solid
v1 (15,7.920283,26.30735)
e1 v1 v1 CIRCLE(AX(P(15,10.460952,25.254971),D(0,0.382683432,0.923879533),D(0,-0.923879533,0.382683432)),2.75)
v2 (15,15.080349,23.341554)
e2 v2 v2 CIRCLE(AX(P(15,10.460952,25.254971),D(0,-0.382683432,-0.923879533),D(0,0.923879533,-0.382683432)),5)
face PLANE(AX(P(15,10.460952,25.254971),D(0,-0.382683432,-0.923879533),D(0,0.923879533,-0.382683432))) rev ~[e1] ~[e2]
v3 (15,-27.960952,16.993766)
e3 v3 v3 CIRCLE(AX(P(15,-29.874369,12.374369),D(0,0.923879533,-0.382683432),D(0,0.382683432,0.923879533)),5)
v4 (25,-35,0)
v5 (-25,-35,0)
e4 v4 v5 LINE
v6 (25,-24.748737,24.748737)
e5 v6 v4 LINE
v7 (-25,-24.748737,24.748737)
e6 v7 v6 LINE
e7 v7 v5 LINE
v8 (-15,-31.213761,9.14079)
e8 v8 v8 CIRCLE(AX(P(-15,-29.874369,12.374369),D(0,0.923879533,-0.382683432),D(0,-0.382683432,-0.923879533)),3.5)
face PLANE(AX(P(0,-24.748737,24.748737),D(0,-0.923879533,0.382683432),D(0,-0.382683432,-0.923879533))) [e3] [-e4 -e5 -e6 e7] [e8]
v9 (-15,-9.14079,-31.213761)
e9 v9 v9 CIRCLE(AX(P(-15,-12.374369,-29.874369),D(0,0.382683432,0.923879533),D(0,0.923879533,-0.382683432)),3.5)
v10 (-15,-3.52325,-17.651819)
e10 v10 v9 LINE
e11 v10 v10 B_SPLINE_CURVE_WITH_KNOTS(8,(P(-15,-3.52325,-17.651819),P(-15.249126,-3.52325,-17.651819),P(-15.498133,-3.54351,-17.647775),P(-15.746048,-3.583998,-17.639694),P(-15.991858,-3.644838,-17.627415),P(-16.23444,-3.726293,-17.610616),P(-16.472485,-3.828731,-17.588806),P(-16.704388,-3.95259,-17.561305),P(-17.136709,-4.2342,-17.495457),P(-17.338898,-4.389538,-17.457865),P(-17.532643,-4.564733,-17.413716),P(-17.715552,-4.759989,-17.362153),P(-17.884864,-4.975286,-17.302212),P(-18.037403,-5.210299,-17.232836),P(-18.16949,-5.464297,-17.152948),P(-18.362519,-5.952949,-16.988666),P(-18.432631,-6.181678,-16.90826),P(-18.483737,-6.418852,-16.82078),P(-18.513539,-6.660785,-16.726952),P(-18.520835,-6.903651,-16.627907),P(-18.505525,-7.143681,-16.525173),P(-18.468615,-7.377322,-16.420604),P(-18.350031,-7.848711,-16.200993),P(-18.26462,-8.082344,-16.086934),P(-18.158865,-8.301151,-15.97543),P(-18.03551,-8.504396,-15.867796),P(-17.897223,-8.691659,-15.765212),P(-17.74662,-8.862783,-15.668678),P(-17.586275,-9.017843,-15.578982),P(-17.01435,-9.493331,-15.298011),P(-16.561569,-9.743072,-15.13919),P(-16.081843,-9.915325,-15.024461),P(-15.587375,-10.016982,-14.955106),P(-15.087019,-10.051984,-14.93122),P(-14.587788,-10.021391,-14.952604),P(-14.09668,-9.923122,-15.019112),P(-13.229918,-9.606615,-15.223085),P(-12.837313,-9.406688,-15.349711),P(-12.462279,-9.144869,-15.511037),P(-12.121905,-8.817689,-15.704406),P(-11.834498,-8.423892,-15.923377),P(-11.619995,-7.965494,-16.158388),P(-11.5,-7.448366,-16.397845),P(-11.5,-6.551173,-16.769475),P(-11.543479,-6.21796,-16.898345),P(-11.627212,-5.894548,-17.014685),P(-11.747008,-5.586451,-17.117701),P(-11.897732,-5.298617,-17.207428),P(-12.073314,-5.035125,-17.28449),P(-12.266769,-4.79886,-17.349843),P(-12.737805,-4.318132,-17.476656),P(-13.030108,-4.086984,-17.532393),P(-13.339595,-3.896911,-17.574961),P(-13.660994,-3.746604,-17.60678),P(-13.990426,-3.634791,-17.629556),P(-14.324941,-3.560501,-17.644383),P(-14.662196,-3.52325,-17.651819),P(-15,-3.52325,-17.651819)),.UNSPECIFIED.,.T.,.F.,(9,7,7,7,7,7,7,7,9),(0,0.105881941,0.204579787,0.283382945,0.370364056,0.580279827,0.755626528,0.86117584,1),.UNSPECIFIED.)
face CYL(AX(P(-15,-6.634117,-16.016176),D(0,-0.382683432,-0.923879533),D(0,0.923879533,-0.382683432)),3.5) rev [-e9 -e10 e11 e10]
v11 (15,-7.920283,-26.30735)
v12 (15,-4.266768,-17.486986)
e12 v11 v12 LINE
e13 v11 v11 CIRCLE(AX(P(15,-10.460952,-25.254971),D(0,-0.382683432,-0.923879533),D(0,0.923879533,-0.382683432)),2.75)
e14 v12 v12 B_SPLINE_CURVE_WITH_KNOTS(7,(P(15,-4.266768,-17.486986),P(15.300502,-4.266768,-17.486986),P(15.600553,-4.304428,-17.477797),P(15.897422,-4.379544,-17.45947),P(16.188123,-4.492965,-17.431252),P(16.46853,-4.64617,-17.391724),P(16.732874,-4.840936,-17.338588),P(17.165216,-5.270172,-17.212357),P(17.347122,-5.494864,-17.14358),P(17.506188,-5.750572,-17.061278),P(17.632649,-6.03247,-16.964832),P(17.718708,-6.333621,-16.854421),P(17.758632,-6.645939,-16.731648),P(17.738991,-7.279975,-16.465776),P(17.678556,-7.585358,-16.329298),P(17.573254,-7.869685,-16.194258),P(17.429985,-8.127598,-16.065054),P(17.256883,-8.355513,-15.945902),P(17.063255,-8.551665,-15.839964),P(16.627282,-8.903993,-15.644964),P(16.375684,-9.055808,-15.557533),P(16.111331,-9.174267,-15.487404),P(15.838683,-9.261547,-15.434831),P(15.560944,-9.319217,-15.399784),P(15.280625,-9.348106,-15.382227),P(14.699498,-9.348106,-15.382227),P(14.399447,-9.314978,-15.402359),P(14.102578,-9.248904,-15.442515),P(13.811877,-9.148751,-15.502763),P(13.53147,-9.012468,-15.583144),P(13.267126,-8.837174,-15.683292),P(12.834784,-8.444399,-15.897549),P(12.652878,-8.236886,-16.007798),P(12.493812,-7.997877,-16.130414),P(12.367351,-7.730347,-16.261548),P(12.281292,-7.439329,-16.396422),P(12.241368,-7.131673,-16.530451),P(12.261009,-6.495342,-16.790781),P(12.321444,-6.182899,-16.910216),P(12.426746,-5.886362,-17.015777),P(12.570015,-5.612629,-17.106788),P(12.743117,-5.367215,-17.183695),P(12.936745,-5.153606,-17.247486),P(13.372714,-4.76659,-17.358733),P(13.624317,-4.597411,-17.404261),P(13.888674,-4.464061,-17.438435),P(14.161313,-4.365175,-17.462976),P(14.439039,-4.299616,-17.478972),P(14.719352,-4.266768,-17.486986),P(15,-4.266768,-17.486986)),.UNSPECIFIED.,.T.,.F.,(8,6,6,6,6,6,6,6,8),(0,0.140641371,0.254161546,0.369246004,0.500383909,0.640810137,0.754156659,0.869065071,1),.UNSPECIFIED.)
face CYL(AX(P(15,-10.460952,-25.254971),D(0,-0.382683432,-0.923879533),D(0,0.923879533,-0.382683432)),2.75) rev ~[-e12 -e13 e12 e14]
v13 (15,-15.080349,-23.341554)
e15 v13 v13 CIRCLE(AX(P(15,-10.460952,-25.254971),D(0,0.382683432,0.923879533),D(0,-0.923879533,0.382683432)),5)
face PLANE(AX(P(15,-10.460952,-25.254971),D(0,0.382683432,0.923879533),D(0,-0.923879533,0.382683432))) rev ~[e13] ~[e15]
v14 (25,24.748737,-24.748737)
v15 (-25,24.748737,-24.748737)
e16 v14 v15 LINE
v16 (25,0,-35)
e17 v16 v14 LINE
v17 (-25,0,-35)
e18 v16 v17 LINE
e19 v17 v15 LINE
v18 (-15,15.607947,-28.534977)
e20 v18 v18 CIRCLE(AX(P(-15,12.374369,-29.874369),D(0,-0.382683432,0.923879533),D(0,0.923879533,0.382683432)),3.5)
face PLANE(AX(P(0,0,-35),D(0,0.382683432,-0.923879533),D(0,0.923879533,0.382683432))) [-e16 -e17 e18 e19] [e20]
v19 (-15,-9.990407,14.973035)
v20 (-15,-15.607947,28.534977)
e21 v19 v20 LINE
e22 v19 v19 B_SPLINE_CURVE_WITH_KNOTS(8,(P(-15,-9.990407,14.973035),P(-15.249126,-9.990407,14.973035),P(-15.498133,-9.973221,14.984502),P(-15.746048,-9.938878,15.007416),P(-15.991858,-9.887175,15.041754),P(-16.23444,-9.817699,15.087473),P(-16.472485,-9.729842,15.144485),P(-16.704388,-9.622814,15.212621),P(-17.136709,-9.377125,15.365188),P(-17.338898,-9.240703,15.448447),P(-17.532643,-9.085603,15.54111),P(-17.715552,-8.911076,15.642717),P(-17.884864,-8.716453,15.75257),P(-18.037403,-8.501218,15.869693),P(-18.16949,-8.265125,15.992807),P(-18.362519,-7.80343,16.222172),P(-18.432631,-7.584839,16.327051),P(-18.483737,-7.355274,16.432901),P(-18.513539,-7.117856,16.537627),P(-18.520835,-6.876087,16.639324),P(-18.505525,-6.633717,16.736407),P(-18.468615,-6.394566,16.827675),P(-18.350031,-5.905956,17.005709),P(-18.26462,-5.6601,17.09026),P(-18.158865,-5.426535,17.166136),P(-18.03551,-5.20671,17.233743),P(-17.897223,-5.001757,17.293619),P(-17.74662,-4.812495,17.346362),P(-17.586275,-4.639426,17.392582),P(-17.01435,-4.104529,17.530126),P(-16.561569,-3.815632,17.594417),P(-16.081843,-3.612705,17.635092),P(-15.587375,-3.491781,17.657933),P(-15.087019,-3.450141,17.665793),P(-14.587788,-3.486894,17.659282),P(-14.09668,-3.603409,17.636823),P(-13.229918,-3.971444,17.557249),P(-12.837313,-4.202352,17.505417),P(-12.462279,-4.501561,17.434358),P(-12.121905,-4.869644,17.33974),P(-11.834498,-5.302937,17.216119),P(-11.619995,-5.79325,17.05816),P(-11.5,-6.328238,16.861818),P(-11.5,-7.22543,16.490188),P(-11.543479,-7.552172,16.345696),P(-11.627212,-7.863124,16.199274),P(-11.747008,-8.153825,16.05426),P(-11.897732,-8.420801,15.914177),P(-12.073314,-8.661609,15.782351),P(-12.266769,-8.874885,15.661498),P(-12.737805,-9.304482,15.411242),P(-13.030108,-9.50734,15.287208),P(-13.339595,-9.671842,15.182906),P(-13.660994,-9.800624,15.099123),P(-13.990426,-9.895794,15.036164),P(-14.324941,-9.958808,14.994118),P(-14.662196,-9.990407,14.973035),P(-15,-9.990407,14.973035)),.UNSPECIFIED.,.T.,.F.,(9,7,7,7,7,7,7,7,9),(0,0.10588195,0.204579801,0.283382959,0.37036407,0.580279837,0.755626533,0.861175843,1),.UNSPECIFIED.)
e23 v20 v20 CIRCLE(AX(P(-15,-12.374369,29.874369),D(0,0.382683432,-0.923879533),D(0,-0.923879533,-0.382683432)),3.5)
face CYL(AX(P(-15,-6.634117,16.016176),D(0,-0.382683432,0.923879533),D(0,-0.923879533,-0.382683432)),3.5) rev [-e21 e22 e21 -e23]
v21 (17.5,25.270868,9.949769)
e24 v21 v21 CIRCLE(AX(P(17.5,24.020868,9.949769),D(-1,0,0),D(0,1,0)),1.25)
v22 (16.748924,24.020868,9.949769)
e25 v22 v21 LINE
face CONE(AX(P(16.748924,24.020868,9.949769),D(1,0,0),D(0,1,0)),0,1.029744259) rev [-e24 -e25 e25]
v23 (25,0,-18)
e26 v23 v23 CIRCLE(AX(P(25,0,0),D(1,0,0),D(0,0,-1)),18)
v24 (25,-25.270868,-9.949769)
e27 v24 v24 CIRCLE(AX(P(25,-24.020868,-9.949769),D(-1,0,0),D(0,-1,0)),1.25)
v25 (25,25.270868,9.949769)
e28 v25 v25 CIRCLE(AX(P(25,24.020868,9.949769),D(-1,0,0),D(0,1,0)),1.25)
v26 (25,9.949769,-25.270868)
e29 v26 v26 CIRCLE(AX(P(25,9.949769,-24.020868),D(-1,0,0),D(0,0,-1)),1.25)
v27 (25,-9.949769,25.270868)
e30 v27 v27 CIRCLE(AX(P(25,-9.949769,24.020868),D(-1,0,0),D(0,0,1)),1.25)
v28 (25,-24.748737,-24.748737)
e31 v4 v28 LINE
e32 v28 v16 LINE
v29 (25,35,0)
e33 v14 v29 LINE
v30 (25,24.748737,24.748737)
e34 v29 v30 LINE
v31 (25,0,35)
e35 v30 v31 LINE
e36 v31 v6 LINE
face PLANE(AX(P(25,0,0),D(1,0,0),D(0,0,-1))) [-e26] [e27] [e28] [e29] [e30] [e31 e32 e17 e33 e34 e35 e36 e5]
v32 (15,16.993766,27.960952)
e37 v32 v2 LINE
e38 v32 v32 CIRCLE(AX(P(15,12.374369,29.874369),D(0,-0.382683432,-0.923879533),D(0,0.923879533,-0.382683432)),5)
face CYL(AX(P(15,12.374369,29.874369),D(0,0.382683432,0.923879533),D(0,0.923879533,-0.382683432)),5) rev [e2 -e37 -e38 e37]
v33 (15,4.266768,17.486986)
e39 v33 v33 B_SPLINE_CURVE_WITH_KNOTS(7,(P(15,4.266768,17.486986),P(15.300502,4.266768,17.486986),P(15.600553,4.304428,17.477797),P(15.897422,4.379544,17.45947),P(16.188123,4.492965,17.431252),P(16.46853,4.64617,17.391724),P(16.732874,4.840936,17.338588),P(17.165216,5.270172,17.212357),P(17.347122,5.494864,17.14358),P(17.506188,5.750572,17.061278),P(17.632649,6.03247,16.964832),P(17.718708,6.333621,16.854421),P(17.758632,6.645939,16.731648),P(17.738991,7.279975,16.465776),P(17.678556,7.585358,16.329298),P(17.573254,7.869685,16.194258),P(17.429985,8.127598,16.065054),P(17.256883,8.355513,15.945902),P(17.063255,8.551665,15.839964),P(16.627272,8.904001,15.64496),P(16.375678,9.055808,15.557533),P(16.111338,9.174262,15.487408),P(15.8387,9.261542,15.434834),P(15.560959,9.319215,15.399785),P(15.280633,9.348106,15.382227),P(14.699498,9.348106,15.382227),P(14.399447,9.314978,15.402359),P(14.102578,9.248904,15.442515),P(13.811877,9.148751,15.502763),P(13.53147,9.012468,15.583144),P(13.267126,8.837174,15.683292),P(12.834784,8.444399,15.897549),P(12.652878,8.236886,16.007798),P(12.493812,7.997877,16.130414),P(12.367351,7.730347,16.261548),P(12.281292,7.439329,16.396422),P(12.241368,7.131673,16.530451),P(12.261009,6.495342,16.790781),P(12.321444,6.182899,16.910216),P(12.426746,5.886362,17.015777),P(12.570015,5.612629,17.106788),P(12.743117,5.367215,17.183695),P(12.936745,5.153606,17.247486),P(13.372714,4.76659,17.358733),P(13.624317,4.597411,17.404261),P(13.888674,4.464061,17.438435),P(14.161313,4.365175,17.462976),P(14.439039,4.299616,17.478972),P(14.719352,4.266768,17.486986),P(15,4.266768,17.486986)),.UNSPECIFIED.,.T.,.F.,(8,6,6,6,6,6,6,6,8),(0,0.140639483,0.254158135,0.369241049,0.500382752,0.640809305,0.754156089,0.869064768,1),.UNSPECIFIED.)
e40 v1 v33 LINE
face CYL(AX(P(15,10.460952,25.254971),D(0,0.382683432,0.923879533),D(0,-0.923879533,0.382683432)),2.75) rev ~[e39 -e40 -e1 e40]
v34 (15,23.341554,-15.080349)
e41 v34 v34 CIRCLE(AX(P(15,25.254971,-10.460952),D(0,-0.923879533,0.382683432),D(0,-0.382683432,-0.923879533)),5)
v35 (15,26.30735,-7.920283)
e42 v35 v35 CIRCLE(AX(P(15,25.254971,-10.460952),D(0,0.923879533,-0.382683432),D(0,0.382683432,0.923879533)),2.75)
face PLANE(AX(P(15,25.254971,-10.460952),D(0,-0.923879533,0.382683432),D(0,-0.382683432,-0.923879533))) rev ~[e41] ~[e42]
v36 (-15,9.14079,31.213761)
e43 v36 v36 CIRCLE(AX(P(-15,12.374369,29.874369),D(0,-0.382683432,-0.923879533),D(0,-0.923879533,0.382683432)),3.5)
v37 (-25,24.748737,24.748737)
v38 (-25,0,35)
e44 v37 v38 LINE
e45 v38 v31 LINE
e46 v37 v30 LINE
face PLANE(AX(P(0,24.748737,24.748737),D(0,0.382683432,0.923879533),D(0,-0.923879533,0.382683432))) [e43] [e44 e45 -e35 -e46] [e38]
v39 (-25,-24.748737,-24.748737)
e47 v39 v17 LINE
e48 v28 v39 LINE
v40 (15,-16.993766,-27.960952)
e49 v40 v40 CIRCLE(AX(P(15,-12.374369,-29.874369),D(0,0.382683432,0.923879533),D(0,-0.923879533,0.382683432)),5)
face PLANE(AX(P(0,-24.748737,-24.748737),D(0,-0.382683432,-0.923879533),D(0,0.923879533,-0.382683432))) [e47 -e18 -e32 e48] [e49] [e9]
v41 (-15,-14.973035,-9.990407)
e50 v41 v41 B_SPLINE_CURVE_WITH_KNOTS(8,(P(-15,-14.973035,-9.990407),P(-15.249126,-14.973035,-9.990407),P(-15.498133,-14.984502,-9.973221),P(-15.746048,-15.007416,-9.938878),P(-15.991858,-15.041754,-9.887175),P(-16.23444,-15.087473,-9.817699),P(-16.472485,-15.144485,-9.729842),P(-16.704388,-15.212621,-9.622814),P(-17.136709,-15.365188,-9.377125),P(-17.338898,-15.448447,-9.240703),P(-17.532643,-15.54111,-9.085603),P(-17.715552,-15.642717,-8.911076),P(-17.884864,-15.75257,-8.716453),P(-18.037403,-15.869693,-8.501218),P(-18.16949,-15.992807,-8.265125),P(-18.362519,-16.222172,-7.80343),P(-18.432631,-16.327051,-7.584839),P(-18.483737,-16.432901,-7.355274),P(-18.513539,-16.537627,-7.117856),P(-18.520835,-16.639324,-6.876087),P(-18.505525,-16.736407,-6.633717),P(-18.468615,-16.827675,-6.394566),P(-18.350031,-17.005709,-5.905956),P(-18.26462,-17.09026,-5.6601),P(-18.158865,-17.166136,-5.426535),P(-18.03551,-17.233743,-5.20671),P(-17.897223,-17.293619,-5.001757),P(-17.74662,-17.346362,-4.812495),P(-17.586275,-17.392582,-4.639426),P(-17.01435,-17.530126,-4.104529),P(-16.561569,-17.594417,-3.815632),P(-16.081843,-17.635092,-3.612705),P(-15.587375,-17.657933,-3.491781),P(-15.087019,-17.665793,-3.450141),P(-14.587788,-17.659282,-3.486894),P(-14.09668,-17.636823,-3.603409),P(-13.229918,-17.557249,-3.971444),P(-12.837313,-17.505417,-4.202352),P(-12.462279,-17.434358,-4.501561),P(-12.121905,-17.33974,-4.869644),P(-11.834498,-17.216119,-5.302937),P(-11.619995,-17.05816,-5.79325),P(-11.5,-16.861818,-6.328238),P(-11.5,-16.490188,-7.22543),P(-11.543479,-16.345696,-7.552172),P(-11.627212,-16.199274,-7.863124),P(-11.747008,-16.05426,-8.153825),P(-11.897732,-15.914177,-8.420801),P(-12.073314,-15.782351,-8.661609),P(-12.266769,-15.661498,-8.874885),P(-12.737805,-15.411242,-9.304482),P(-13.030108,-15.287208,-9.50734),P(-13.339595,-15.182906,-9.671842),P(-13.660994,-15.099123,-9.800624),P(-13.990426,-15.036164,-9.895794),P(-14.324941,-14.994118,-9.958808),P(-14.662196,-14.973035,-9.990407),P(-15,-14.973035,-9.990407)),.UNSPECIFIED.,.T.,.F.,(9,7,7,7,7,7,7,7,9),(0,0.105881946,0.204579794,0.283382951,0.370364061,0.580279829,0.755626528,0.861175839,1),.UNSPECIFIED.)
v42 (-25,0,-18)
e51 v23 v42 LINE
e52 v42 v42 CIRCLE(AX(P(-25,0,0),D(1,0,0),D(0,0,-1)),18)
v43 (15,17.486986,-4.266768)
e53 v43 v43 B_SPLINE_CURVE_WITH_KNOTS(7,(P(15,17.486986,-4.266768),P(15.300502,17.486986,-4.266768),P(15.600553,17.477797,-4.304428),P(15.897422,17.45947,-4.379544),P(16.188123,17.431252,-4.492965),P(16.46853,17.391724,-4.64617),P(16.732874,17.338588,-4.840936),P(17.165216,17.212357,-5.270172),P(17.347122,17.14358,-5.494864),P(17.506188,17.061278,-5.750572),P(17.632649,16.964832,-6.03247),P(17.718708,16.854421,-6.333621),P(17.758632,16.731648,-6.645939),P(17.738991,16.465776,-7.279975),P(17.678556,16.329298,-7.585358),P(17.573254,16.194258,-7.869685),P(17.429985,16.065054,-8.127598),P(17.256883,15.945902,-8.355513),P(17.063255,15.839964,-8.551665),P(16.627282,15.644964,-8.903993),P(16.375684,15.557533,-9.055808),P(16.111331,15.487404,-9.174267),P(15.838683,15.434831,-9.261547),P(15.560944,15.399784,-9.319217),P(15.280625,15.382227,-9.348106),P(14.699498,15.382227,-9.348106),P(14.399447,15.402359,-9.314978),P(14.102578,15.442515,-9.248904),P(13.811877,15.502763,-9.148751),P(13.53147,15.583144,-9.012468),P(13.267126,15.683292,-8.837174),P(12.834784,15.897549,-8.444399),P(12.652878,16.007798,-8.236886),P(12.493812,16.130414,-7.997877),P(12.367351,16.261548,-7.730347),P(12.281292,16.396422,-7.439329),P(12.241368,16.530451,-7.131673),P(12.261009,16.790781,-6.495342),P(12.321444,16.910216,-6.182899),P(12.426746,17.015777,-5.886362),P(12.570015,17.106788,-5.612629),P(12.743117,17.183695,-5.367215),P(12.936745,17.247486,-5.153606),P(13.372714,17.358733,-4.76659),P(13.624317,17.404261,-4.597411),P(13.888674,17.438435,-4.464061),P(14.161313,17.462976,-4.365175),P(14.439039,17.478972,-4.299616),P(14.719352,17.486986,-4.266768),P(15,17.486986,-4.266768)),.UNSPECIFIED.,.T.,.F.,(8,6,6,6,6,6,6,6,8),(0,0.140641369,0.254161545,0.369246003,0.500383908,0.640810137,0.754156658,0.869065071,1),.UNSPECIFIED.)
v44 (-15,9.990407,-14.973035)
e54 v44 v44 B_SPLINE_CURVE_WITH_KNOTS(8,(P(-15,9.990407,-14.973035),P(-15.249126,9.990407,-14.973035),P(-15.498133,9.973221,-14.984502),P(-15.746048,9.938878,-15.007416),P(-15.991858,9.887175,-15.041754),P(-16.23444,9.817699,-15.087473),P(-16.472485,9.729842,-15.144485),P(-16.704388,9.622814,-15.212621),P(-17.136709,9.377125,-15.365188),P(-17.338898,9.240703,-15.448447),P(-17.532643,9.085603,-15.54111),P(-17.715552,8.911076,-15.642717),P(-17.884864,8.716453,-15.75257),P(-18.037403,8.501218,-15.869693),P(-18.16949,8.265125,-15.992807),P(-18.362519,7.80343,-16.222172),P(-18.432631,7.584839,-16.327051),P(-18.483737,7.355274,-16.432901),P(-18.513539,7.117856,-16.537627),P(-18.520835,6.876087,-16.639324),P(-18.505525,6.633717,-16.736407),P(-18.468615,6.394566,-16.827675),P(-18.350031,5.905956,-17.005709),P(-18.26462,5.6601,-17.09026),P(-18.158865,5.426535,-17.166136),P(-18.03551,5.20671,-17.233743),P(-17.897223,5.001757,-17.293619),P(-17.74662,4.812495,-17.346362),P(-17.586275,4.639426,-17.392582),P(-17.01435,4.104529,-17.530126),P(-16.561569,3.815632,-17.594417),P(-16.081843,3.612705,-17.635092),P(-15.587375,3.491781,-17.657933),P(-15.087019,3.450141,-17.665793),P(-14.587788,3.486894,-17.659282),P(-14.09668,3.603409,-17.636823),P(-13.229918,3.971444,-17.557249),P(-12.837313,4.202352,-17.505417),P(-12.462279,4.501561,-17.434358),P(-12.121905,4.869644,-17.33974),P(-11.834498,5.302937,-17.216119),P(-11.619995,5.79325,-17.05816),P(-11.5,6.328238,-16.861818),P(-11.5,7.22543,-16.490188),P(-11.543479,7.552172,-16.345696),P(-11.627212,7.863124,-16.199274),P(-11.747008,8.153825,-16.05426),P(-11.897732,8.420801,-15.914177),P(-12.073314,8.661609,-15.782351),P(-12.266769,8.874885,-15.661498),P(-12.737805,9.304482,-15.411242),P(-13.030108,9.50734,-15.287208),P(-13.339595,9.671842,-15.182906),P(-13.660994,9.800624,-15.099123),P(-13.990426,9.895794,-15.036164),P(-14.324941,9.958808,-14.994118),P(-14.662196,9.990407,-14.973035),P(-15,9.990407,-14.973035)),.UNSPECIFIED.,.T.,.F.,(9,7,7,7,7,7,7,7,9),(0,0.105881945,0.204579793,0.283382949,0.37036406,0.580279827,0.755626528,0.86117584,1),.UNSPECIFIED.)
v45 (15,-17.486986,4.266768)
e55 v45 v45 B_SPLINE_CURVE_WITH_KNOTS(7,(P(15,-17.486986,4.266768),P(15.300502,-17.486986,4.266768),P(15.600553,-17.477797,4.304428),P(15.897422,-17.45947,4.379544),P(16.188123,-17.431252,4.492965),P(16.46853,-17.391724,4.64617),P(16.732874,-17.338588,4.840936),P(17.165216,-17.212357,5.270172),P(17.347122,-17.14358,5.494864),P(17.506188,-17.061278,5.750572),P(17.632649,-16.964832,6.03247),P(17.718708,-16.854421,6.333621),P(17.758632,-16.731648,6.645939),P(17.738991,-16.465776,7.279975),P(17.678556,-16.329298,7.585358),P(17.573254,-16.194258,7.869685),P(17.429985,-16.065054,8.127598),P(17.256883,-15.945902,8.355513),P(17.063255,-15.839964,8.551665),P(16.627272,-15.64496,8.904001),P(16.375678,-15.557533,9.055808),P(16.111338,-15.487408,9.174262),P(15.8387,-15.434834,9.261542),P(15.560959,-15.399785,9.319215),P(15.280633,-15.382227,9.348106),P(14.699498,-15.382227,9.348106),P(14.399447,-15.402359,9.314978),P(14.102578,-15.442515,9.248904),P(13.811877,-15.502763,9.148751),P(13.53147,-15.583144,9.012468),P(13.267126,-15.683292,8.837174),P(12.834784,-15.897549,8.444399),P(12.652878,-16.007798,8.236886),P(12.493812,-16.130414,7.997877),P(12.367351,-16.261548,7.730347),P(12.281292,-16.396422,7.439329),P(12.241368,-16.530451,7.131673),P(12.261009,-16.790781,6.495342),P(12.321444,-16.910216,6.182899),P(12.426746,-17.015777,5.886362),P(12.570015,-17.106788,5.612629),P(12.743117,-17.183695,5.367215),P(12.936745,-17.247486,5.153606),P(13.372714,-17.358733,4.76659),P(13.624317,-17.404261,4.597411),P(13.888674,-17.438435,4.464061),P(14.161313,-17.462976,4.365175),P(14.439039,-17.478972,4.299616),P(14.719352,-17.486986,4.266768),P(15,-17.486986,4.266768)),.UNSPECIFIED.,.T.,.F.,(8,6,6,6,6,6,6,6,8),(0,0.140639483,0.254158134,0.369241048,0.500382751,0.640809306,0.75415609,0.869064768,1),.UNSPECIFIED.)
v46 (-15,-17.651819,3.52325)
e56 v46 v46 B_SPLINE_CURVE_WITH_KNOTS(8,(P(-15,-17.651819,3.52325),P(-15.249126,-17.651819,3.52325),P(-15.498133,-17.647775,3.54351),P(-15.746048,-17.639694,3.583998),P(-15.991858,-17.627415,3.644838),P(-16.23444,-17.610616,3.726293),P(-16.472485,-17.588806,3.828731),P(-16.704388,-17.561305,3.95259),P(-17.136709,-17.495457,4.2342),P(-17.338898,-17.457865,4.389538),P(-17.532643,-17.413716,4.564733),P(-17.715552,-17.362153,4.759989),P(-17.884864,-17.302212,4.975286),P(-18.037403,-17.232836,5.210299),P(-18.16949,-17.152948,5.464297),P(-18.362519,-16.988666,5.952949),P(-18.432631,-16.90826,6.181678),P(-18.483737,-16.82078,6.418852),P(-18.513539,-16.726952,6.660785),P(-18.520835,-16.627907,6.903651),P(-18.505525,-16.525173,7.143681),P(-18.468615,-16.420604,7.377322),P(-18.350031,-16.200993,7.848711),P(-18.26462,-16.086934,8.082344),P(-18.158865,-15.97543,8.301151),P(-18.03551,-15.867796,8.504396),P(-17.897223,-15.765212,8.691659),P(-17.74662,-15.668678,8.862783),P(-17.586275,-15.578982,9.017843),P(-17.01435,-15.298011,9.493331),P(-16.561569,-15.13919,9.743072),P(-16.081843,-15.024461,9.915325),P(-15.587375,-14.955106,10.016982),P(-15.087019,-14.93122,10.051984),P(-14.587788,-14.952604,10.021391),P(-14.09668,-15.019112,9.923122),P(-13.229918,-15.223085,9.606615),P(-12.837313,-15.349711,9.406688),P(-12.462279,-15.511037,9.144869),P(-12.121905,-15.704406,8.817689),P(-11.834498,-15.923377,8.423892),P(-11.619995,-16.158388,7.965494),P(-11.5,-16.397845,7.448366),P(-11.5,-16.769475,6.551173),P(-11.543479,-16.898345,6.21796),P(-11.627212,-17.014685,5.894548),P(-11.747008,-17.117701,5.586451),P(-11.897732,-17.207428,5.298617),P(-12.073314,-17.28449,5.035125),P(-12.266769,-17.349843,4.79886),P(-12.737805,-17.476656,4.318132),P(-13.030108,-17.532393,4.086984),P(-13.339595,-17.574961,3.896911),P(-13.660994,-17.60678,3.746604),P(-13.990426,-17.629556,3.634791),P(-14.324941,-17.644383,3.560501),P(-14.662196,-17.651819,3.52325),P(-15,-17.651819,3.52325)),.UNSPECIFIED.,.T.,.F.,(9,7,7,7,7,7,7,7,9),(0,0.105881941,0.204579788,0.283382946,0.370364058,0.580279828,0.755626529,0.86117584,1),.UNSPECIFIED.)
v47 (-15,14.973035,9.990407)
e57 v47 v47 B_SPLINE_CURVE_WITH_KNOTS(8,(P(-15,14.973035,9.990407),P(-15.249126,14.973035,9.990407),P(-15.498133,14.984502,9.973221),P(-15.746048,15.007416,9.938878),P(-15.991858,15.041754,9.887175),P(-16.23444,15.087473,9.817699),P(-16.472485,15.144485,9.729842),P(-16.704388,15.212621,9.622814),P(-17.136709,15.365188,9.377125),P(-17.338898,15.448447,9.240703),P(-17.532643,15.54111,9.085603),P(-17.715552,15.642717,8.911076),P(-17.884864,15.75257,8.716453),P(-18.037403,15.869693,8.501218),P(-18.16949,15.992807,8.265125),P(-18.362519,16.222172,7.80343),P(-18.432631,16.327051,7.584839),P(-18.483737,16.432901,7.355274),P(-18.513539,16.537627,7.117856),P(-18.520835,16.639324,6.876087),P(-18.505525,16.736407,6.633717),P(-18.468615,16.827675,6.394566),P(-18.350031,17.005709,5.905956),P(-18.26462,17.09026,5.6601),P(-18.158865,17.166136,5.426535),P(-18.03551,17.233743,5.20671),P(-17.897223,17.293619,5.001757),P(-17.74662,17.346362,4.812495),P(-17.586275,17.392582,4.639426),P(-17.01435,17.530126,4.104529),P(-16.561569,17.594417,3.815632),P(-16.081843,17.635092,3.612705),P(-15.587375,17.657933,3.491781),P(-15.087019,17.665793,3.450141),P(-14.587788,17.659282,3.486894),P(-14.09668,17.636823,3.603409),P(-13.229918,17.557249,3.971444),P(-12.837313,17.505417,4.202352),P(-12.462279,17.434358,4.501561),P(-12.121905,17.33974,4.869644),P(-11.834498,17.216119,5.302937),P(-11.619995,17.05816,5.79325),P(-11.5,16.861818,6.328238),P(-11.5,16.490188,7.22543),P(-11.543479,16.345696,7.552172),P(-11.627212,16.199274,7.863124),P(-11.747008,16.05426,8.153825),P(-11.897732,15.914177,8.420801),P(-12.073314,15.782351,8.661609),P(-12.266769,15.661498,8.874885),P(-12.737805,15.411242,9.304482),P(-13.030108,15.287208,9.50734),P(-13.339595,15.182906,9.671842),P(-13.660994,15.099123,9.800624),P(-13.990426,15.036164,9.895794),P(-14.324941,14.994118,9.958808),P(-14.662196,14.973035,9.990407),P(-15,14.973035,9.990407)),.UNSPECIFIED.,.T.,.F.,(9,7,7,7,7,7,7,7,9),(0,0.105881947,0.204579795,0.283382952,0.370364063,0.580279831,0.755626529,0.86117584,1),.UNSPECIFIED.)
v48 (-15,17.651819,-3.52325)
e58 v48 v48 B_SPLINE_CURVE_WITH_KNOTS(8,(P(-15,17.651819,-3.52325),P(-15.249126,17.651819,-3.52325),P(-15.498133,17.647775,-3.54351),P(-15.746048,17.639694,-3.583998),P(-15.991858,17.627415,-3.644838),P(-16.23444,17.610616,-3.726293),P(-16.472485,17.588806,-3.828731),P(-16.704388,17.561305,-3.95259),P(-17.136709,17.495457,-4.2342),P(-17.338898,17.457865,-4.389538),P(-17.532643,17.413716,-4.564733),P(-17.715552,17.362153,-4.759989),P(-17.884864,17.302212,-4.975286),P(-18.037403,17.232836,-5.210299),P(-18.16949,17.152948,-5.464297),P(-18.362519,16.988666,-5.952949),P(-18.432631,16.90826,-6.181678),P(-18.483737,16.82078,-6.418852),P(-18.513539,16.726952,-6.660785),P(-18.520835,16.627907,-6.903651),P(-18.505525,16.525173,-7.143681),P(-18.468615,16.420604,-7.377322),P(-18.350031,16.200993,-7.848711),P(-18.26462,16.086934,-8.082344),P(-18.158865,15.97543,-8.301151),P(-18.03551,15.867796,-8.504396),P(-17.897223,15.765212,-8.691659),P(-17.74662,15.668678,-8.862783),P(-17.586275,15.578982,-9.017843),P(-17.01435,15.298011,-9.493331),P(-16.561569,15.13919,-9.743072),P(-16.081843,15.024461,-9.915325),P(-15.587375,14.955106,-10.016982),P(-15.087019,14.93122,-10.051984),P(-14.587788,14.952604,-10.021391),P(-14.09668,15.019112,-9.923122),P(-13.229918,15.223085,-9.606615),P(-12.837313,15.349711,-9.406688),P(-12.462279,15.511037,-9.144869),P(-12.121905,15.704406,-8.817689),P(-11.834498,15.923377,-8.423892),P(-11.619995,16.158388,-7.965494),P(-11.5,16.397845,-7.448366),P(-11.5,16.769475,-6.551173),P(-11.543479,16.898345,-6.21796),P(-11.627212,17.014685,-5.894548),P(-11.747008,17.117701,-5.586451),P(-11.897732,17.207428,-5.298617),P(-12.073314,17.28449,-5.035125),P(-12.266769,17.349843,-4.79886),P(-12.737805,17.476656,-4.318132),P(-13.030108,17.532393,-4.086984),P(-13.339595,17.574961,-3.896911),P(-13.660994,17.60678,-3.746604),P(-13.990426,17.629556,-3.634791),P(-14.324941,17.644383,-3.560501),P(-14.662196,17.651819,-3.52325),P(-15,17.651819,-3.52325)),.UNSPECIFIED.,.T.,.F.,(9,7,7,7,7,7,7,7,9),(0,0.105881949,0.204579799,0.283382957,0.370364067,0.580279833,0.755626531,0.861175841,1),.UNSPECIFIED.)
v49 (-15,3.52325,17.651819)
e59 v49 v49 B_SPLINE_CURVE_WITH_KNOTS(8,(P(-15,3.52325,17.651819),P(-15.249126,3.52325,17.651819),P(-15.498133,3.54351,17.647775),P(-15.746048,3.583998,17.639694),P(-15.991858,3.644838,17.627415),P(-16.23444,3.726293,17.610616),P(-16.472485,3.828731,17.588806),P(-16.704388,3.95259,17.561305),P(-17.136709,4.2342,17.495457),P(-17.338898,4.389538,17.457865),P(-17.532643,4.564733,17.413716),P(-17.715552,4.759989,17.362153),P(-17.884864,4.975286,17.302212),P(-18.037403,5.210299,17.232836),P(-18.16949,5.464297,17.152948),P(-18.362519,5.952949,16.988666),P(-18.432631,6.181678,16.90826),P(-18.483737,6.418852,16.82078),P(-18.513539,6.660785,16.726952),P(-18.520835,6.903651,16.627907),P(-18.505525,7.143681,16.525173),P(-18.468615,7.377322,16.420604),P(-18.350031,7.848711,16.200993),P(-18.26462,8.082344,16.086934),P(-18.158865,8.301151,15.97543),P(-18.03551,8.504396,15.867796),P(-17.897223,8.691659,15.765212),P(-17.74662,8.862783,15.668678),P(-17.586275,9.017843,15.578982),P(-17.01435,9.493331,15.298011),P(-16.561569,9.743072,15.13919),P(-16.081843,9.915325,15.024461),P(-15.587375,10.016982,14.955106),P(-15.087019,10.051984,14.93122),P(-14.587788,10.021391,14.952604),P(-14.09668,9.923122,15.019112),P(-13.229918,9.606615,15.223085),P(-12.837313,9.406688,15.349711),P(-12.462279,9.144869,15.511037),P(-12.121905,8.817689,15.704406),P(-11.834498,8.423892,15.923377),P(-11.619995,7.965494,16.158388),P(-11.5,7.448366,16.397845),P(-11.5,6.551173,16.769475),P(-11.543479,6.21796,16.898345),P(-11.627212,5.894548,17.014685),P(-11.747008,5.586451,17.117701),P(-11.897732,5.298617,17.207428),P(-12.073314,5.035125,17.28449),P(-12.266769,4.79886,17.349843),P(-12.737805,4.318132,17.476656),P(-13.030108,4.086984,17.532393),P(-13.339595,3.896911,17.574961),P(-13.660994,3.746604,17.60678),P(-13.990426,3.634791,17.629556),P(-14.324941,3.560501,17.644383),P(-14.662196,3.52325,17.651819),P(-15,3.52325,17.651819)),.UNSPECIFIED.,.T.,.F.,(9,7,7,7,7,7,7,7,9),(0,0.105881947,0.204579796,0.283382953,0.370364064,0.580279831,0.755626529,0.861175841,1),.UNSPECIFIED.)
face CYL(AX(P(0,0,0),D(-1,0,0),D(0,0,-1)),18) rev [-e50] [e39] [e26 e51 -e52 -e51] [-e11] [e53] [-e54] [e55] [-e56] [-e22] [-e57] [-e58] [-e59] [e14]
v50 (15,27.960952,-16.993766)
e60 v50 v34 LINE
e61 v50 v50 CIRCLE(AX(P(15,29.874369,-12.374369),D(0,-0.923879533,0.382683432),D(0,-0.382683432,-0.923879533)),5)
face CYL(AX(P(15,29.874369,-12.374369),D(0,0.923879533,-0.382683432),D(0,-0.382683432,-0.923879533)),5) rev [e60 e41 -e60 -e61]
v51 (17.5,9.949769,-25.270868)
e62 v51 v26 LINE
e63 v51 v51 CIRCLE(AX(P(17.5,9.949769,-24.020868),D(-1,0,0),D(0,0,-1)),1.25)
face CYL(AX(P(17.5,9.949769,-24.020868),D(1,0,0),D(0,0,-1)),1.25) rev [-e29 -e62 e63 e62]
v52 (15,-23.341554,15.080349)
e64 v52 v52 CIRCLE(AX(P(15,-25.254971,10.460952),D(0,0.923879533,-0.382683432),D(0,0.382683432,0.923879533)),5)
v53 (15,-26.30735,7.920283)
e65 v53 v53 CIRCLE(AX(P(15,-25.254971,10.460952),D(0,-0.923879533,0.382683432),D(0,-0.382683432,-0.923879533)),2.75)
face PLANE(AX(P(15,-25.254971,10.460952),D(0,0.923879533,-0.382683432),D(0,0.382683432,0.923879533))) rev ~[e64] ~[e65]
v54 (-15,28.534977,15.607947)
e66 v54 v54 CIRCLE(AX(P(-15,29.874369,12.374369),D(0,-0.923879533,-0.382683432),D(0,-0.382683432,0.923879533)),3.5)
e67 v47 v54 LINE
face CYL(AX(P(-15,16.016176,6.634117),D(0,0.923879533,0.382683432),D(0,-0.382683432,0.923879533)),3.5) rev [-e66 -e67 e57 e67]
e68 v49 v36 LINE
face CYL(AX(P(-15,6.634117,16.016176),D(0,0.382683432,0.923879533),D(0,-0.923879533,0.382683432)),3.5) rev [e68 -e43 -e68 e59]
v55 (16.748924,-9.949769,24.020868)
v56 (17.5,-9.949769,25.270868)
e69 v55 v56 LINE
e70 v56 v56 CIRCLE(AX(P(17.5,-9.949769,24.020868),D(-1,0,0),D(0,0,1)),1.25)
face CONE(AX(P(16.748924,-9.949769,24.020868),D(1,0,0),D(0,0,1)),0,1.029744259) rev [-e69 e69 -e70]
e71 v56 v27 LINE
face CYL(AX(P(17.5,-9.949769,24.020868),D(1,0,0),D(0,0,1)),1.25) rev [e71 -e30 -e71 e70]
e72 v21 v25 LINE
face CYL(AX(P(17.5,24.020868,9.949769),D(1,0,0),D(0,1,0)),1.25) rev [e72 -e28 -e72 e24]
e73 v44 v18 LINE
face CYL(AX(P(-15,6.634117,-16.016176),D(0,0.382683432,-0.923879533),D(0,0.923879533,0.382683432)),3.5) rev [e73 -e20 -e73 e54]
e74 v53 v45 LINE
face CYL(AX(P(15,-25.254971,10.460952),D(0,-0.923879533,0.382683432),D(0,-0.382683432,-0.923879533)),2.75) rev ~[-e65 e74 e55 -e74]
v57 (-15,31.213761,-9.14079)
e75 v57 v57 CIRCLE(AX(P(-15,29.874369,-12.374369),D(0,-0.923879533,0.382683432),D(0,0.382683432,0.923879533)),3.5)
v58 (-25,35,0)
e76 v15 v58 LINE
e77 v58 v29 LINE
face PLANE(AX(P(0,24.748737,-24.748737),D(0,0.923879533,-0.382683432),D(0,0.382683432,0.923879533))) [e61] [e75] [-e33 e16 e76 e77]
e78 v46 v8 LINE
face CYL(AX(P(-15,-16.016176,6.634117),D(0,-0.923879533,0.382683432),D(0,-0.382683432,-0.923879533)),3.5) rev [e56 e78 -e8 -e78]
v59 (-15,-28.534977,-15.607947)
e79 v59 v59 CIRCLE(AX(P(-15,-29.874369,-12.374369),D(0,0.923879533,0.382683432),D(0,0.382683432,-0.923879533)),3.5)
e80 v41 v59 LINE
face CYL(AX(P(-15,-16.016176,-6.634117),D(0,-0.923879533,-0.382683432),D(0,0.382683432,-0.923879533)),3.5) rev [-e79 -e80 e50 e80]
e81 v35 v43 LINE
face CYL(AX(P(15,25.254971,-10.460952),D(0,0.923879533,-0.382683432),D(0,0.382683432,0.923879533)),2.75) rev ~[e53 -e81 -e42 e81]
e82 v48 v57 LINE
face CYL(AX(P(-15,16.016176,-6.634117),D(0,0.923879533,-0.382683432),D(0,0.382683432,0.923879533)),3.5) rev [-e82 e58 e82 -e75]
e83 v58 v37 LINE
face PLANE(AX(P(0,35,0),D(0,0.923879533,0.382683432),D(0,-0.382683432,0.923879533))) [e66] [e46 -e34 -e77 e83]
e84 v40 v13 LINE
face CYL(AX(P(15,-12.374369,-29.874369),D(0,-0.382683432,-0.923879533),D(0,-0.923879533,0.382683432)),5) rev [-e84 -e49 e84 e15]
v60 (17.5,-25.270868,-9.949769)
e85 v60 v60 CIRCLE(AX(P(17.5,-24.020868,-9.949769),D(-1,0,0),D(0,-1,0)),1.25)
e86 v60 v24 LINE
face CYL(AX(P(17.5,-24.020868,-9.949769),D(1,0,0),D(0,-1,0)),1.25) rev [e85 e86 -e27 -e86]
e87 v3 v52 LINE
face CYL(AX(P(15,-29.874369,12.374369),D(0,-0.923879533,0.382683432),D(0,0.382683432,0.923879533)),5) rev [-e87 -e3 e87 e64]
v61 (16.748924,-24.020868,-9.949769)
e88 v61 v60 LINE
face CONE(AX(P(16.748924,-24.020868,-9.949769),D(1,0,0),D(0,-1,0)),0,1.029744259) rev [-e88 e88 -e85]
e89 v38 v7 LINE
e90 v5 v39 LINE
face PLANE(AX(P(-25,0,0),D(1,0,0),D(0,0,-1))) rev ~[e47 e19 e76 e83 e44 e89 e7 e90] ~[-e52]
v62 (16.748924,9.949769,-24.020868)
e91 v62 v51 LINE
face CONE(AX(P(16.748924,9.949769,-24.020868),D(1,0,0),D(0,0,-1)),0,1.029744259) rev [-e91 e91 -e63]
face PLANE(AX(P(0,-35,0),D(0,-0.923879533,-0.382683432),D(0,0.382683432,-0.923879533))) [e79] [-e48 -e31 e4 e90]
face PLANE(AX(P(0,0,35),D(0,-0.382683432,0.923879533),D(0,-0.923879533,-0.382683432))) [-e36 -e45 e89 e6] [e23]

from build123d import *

# Parameters (mm, degrees)
SKETCH_1_R               = 18
EXTRUDE_1_DEPTH          = 25
SKETCH_2_R               = 5
CUT_EXTRUDE_1_DEPTH      = 5
SKETCH_4_R               = 2.75
CUT_EXTRUDE_2_DEPTH      = 23
PATTERN_CIRCULAR_1_COUNT = 8
PATTERN_CIRCULAR_2_COUNT = 4
PATTERN_CIRCULAR_3_COUNT = 4


with BuildPart() as part:
    # 草图1 → 凸台-拉伸1 (new, symmetric)
    with BuildSketch(Plane(origin=(0, 0, 0), x_dir=(0, 0, -1), z_dir=(1, 0, 0))):
        Polygon((24.748737342, 24.748737342), (0, 35), (-24.748737342, 24.748737342), (-35, 0), (-24.748737342, -24.748737342), (0, -35), (24.748737342, -24.748737342), (35, 0), align=None)
        Circle(SKETCH_1_R, mode=Mode.SUBTRACT)
    extrude(amount=EXTRUDE_1_DEPTH, both=True)

    # 草图2 → 切除-拉伸1 (cut)
    with BuildSketch(Plane(origin=(0, -29.874368671, 12.374368671), x_dir=(1, 0, 0), z_dir=(0, 0.9238795325112868, -0.3826834323650897))):
        with Locations(Location((15, 0, 0), (0, 0, 270))):
            Circle(SKETCH_2_R)
    cut_extrude_1 = extrude(amount=CUT_EXTRUDE_1_DEPTH, mode=Mode.SUBTRACT)

    # 草图4 → 切除-拉伸2 (cut)
    with BuildSketch(Plane(origin=(0, -25.254971008, 10.460951509), x_dir=(1, 0, 0), z_dir=(0, -0.9238795325112867, 0.38268343236508956))):
        with Locations(Location((15, 0, 0), (0, 0, 270))):
            Circle(SKETCH_4_R)
    cut_extrude_2 = extrude(amount=-CUT_EXTRUDE_2_DEPTH, mode=Mode.SUBTRACT)

    # 草图6 → M8x1.0 螺纹孔1 (revolve, cut)
    with BuildSketch(Plane(origin=(-15, -12.374368671, 29.874368671), x_dir=(0, -0.9238795325112867, -0.38268343236508995), z_dir=(1, 0, 0))):
        Polygon((0, 0), (0, 17.103012167), (3.5, 15), (3.5, 0), align=None)
    m8x1_0_1 = revolve(axis=Axis((-15, -14.804408466, 35.741003702), (0, 0.38268343236508995, -0.9238795325112867)), mode=Mode.SUBTRACT)

    # 阵列(圆周)1: M8x1.0 螺纹孔1 ×8 about axis
    pattern_circular_1_axis = Axis((25, 0, 0), (-1, 0, 0))
    for i in range(1, PATTERN_CIRCULAR_1_COUNT):
        add(m8x1_0_1.rotate(pattern_circular_1_axis, i * 360 / PATTERN_CIRCULAR_1_COUNT), mode=Mode.SUBTRACT)

    # 阵列(圆周)2: 切除-拉伸1, 切除-拉伸2 ×4 about axis
    pattern_circular_2_axis = Axis((0, 0, 0), (1, 0, 0))
    add([cut_extrude_1.rotate(pattern_circular_2_axis, i * 360 / PATTERN_CIRCULAR_2_COUNT) for i in range(1, PATTERN_CIRCULAR_2_COUNT)], mode=Mode.SUBTRACT)
    add([cut_extrude_2.rotate(pattern_circular_2_axis, i * 360 / PATTERN_CIRCULAR_2_COUNT) for i in range(1, PATTERN_CIRCULAR_2_COUNT)], mode=Mode.SUBTRACT)

    # 草图8 → M3x0.5 螺纹孔1 (revolve, cut)
    with BuildSketch(Plane(origin=(25, 9.949769241, -24.020867845), x_dir=(0, 0, -1), z_dir=(0, 1, 0))):
        Polygon((0, 0), (0, 8.251075774), (1.25, 7.5), (1.25, 0), align=None)
    m3x0_5_1 = revolve(axis=Axis((31.35, 9.949769241, -24.020867845), (-1, 0, 0)), mode=Mode.SUBTRACT)

    # 阵列(圆周)3: M3x0.5 螺纹孔1 ×4 about axis
    pattern_circular_3_axis = Axis((0, 0, 0), (1, 0, 0))
    for i in range(1, PATTERN_CIRCULAR_3_COUNT):
        add(m3x0_5_1.rotate(pattern_circular_3_axis, i * 360 / PATTERN_CIRCULAR_3_COUNT), mode=Mode.SUBTRACT)


solid = part.part
